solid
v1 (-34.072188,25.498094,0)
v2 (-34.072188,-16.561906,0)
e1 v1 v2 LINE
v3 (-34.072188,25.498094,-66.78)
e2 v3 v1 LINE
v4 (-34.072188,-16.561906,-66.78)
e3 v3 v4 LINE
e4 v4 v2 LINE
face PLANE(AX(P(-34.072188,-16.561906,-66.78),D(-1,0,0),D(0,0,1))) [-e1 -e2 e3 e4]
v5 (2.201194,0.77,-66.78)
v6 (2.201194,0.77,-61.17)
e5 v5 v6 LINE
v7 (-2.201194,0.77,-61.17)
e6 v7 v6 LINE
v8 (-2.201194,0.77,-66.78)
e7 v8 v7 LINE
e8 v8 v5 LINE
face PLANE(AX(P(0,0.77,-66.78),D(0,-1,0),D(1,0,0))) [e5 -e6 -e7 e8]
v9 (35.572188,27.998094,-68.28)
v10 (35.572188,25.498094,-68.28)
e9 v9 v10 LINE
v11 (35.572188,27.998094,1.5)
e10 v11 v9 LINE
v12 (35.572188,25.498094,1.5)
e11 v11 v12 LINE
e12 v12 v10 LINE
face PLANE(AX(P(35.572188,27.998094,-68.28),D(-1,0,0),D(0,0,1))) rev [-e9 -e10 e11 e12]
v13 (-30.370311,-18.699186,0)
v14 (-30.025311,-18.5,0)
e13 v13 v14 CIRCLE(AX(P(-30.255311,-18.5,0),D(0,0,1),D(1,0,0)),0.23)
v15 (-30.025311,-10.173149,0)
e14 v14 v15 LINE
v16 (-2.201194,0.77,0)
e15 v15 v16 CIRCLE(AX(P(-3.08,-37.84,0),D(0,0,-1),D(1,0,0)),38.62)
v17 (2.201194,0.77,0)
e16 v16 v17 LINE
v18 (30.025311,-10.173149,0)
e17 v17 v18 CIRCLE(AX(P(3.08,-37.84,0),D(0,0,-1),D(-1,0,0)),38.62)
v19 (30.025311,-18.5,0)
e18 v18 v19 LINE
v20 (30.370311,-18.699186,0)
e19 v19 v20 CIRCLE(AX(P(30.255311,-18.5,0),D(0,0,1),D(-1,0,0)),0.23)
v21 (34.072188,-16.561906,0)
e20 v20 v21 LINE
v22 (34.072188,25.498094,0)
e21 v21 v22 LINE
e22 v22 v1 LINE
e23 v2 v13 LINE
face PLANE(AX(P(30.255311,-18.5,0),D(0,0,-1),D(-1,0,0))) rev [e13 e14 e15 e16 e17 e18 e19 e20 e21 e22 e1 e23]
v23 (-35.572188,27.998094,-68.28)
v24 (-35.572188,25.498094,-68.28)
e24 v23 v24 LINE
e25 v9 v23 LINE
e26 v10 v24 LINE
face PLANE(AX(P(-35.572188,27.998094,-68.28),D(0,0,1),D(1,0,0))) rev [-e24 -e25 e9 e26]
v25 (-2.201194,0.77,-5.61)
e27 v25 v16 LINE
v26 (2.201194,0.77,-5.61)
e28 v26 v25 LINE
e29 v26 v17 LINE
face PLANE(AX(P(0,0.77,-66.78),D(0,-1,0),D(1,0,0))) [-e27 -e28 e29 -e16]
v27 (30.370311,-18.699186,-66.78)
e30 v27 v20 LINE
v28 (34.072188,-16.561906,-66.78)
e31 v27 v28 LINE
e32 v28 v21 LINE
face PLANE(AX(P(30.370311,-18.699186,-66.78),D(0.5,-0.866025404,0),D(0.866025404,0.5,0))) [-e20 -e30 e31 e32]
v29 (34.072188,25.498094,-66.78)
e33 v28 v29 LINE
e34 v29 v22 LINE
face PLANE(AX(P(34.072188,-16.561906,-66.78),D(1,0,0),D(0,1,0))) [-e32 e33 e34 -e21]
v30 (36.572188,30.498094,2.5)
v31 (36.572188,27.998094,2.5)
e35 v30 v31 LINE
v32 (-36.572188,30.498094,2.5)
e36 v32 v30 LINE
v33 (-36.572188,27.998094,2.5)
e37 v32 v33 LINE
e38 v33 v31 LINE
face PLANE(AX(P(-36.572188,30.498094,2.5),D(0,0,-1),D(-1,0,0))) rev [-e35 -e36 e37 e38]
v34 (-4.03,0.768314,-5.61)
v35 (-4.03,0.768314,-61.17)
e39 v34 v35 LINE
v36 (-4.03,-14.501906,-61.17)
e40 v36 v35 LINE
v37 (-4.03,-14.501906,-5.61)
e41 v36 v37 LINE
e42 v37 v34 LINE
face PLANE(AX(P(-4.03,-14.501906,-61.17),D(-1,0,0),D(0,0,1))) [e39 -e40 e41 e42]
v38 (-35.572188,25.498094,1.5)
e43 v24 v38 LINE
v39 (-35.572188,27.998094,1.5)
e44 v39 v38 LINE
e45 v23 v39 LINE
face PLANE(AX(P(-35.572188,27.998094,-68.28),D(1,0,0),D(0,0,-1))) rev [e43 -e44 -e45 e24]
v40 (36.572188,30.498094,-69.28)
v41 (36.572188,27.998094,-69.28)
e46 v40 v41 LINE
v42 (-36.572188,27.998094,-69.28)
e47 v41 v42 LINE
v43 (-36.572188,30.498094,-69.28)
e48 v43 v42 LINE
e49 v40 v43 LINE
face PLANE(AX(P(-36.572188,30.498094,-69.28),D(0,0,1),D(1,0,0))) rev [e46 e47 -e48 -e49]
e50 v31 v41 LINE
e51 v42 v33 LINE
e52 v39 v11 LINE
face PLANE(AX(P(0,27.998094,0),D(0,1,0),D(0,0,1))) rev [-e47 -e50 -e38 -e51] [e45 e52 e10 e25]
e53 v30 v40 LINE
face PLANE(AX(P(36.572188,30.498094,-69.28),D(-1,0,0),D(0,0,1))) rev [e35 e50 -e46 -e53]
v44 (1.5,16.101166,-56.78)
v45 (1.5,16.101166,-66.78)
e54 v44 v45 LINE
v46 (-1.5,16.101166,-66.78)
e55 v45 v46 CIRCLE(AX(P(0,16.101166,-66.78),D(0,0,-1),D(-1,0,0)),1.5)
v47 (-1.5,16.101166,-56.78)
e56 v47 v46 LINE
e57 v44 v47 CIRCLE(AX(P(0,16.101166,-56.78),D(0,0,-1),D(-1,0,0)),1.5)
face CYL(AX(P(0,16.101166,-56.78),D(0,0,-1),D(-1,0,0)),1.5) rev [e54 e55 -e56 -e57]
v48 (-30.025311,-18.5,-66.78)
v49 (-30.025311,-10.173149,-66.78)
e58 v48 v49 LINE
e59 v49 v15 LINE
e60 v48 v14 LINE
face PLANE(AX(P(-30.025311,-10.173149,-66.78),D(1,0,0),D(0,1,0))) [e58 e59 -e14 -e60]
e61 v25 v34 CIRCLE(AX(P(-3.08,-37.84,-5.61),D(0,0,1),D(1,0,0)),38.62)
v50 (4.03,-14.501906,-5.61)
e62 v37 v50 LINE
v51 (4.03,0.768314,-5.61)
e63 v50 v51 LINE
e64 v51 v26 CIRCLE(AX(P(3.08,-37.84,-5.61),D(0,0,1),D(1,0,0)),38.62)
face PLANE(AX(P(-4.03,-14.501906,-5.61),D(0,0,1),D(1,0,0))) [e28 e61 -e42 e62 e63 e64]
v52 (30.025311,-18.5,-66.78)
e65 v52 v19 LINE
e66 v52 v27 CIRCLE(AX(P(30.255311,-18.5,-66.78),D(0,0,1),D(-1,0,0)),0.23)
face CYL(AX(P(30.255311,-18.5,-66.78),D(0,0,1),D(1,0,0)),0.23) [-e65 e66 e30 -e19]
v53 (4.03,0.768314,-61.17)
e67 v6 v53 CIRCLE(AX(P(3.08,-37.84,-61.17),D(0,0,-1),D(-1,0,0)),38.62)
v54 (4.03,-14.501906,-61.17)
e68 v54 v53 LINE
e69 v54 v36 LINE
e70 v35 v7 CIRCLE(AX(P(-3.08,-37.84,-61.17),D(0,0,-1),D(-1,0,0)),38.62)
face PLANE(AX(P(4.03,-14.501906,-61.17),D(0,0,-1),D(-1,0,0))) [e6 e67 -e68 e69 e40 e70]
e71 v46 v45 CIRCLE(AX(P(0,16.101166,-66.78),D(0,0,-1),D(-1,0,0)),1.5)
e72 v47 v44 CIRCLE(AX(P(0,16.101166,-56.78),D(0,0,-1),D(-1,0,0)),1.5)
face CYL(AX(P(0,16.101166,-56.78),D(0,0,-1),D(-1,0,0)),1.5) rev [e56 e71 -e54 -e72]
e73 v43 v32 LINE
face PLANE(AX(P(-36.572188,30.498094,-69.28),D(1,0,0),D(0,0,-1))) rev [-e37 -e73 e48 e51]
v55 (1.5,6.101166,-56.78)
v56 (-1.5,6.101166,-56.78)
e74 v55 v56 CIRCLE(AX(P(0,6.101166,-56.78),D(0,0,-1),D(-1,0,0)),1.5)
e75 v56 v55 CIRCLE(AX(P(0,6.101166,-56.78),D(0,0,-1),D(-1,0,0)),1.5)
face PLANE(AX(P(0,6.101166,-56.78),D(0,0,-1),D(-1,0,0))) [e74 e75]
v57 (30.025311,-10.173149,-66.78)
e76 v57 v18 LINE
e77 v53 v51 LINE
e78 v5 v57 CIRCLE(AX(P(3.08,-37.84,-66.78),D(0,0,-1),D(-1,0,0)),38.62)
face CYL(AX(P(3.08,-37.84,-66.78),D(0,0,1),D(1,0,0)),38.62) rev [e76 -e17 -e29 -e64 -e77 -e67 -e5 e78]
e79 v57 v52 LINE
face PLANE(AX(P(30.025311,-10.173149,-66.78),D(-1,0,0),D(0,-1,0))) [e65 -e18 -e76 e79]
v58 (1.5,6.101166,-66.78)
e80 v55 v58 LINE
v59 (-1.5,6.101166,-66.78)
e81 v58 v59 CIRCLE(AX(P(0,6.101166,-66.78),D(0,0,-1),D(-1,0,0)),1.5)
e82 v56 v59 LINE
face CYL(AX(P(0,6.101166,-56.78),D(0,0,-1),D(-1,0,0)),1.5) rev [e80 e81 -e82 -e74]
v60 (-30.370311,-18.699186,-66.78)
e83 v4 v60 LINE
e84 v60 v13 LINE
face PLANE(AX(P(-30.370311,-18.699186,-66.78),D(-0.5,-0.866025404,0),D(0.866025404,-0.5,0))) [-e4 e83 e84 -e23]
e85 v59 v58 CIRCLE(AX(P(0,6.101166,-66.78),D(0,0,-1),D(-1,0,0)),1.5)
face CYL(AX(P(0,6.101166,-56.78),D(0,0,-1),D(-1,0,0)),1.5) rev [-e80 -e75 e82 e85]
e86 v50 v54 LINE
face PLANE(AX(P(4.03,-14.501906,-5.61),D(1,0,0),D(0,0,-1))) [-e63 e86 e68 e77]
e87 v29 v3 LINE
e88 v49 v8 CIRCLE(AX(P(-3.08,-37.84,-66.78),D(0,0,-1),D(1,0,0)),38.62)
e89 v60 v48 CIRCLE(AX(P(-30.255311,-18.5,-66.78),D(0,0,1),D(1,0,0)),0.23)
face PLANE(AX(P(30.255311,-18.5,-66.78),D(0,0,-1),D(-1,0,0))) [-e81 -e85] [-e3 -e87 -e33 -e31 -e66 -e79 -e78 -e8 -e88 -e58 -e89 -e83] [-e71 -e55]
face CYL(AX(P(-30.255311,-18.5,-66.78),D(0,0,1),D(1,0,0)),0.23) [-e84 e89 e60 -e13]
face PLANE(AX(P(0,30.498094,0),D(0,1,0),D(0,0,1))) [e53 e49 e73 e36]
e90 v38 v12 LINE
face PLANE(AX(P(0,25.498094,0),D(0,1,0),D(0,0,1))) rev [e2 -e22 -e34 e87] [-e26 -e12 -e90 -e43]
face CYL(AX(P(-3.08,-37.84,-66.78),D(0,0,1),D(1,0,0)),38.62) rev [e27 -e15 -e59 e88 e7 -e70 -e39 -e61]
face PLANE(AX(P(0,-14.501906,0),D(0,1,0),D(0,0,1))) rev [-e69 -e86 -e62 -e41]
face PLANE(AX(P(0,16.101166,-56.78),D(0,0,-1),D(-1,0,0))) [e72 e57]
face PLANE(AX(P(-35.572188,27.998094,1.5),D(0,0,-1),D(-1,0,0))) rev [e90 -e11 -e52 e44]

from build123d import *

# Parameters (mm, degrees)
BOSS_EXTRUDE1_DEPTH = 66.78
SKETCH3_W           = 8.06
SKETCH3_H           = 55.56
BOSS_EXTRUDE2_DEPTH = 40
SKETCH5_W           = 71.144376366
SKETCH5_H           = 69.78
BOSS_EXTRUDE4_DEPTH = 2.5
SKETCH6_W           = 73.144376366
SKETCH6_H           = 71.78
BOSS_EXTRUDE5_DEPTH = 2.5
SKETCH7_R           = 1.5
CUT_EXTRUDE1_DEPTH  = 10


with BuildPart() as part:
    # Sketch1 → Boss-Extrude1 (new body)
    with BuildSketch(Plane.XY):
        with BuildLine():
            Line((-34.072188183, 25.498094011), (34.072188183, 25.498094011))
            Line((34.072188183, 25.498094011), (34.072188183, -16.561905989))
            Line((34.072188183, -16.561905989), (30.370310886, -18.699185843))
            ThreePointArc((30.370310886, -18.699185843), (30.140310886, -18.699185843), (30.025310886, -18.5))
            Line((30.025310886, -18.5), (30.025310886, -10.173149416))
            ThreePointArc((30.025310886, -10.173149416), (17.215197166, -1.899763481), (2.201193992, 0.77))
            Line((2.201193992, 0.77), (0, 0.77))
            Line((0, 0.77), (-2.201193992, 0.77))
            ThreePointArc((-2.201193992, 0.77), (-17.215197166, -1.899763481), (-30.025310886, -10.173149416))
            Line((-30.025310886, -10.173149416), (-30.025310886, -18.5))
            ThreePointArc((-30.025310886, -18.5), (-30.140310886, -18.699185843), (-30.370310886, -18.699185843))
            Line((-30.370310886, -18.699185843), (-34.072188183, -16.561905989))
            Line((-34.072188183, -16.561905989), (-34.072188183, 25.498094011))
        make_face()
    extrude(amount=-BOSS_EXTRUDE1_DEPTH)

    # Sketch3 → Boss-Extrude2 (add)
    with BuildSketch(Plane(origin=(0, 25.498094011, 0), x_dir=(1, 0, 0), z_dir=(0, 1, 0))):
        with Locations((0, 33.39)):
            Rectangle(SKETCH3_W, SKETCH3_H)
    extrude(amount=-BOSS_EXTRUDE2_DEPTH)

    # Sketch5 → Boss-Extrude4 (add)
    with BuildSketch(Plane(origin=(0, 25.498094011, 0), x_dir=(1, 0, 0), z_dir=(0, 1, 0))):
        with Locations((0, 33.39)):
            Rectangle(SKETCH5_W, SKETCH5_H)
    extrude(amount=BOSS_EXTRUDE4_DEPTH)

    # Sketch6 → Boss-Extrude5 (add)
    with BuildSketch(Plane(origin=(0, 27.998094011, 0), x_dir=(1, 0, 0), z_dir=(0, 1, 0))):
        with Locations((0, 33.39)):
            Rectangle(SKETCH6_W, SKETCH6_H)
    extrude(amount=BOSS_EXTRUDE5_DEPTH)

    # Sketch7 → Cut-Extrude1 (cut)
    with BuildSketch(Plane(origin=(0, 0, -66.78), x_dir=(-1, 0, 0), z_dir=(0, 0, -1))):
        with Locations((0, 6.101165809)):
            Circle(SKETCH7_R)
        with Locations((0, 16.101165809)):
            Circle(SKETCH7_R)
    extrude(amount=-CUT_EXTRUDE1_DEPTH, mode=Mode.SUBTRACT)


solid = part.part
